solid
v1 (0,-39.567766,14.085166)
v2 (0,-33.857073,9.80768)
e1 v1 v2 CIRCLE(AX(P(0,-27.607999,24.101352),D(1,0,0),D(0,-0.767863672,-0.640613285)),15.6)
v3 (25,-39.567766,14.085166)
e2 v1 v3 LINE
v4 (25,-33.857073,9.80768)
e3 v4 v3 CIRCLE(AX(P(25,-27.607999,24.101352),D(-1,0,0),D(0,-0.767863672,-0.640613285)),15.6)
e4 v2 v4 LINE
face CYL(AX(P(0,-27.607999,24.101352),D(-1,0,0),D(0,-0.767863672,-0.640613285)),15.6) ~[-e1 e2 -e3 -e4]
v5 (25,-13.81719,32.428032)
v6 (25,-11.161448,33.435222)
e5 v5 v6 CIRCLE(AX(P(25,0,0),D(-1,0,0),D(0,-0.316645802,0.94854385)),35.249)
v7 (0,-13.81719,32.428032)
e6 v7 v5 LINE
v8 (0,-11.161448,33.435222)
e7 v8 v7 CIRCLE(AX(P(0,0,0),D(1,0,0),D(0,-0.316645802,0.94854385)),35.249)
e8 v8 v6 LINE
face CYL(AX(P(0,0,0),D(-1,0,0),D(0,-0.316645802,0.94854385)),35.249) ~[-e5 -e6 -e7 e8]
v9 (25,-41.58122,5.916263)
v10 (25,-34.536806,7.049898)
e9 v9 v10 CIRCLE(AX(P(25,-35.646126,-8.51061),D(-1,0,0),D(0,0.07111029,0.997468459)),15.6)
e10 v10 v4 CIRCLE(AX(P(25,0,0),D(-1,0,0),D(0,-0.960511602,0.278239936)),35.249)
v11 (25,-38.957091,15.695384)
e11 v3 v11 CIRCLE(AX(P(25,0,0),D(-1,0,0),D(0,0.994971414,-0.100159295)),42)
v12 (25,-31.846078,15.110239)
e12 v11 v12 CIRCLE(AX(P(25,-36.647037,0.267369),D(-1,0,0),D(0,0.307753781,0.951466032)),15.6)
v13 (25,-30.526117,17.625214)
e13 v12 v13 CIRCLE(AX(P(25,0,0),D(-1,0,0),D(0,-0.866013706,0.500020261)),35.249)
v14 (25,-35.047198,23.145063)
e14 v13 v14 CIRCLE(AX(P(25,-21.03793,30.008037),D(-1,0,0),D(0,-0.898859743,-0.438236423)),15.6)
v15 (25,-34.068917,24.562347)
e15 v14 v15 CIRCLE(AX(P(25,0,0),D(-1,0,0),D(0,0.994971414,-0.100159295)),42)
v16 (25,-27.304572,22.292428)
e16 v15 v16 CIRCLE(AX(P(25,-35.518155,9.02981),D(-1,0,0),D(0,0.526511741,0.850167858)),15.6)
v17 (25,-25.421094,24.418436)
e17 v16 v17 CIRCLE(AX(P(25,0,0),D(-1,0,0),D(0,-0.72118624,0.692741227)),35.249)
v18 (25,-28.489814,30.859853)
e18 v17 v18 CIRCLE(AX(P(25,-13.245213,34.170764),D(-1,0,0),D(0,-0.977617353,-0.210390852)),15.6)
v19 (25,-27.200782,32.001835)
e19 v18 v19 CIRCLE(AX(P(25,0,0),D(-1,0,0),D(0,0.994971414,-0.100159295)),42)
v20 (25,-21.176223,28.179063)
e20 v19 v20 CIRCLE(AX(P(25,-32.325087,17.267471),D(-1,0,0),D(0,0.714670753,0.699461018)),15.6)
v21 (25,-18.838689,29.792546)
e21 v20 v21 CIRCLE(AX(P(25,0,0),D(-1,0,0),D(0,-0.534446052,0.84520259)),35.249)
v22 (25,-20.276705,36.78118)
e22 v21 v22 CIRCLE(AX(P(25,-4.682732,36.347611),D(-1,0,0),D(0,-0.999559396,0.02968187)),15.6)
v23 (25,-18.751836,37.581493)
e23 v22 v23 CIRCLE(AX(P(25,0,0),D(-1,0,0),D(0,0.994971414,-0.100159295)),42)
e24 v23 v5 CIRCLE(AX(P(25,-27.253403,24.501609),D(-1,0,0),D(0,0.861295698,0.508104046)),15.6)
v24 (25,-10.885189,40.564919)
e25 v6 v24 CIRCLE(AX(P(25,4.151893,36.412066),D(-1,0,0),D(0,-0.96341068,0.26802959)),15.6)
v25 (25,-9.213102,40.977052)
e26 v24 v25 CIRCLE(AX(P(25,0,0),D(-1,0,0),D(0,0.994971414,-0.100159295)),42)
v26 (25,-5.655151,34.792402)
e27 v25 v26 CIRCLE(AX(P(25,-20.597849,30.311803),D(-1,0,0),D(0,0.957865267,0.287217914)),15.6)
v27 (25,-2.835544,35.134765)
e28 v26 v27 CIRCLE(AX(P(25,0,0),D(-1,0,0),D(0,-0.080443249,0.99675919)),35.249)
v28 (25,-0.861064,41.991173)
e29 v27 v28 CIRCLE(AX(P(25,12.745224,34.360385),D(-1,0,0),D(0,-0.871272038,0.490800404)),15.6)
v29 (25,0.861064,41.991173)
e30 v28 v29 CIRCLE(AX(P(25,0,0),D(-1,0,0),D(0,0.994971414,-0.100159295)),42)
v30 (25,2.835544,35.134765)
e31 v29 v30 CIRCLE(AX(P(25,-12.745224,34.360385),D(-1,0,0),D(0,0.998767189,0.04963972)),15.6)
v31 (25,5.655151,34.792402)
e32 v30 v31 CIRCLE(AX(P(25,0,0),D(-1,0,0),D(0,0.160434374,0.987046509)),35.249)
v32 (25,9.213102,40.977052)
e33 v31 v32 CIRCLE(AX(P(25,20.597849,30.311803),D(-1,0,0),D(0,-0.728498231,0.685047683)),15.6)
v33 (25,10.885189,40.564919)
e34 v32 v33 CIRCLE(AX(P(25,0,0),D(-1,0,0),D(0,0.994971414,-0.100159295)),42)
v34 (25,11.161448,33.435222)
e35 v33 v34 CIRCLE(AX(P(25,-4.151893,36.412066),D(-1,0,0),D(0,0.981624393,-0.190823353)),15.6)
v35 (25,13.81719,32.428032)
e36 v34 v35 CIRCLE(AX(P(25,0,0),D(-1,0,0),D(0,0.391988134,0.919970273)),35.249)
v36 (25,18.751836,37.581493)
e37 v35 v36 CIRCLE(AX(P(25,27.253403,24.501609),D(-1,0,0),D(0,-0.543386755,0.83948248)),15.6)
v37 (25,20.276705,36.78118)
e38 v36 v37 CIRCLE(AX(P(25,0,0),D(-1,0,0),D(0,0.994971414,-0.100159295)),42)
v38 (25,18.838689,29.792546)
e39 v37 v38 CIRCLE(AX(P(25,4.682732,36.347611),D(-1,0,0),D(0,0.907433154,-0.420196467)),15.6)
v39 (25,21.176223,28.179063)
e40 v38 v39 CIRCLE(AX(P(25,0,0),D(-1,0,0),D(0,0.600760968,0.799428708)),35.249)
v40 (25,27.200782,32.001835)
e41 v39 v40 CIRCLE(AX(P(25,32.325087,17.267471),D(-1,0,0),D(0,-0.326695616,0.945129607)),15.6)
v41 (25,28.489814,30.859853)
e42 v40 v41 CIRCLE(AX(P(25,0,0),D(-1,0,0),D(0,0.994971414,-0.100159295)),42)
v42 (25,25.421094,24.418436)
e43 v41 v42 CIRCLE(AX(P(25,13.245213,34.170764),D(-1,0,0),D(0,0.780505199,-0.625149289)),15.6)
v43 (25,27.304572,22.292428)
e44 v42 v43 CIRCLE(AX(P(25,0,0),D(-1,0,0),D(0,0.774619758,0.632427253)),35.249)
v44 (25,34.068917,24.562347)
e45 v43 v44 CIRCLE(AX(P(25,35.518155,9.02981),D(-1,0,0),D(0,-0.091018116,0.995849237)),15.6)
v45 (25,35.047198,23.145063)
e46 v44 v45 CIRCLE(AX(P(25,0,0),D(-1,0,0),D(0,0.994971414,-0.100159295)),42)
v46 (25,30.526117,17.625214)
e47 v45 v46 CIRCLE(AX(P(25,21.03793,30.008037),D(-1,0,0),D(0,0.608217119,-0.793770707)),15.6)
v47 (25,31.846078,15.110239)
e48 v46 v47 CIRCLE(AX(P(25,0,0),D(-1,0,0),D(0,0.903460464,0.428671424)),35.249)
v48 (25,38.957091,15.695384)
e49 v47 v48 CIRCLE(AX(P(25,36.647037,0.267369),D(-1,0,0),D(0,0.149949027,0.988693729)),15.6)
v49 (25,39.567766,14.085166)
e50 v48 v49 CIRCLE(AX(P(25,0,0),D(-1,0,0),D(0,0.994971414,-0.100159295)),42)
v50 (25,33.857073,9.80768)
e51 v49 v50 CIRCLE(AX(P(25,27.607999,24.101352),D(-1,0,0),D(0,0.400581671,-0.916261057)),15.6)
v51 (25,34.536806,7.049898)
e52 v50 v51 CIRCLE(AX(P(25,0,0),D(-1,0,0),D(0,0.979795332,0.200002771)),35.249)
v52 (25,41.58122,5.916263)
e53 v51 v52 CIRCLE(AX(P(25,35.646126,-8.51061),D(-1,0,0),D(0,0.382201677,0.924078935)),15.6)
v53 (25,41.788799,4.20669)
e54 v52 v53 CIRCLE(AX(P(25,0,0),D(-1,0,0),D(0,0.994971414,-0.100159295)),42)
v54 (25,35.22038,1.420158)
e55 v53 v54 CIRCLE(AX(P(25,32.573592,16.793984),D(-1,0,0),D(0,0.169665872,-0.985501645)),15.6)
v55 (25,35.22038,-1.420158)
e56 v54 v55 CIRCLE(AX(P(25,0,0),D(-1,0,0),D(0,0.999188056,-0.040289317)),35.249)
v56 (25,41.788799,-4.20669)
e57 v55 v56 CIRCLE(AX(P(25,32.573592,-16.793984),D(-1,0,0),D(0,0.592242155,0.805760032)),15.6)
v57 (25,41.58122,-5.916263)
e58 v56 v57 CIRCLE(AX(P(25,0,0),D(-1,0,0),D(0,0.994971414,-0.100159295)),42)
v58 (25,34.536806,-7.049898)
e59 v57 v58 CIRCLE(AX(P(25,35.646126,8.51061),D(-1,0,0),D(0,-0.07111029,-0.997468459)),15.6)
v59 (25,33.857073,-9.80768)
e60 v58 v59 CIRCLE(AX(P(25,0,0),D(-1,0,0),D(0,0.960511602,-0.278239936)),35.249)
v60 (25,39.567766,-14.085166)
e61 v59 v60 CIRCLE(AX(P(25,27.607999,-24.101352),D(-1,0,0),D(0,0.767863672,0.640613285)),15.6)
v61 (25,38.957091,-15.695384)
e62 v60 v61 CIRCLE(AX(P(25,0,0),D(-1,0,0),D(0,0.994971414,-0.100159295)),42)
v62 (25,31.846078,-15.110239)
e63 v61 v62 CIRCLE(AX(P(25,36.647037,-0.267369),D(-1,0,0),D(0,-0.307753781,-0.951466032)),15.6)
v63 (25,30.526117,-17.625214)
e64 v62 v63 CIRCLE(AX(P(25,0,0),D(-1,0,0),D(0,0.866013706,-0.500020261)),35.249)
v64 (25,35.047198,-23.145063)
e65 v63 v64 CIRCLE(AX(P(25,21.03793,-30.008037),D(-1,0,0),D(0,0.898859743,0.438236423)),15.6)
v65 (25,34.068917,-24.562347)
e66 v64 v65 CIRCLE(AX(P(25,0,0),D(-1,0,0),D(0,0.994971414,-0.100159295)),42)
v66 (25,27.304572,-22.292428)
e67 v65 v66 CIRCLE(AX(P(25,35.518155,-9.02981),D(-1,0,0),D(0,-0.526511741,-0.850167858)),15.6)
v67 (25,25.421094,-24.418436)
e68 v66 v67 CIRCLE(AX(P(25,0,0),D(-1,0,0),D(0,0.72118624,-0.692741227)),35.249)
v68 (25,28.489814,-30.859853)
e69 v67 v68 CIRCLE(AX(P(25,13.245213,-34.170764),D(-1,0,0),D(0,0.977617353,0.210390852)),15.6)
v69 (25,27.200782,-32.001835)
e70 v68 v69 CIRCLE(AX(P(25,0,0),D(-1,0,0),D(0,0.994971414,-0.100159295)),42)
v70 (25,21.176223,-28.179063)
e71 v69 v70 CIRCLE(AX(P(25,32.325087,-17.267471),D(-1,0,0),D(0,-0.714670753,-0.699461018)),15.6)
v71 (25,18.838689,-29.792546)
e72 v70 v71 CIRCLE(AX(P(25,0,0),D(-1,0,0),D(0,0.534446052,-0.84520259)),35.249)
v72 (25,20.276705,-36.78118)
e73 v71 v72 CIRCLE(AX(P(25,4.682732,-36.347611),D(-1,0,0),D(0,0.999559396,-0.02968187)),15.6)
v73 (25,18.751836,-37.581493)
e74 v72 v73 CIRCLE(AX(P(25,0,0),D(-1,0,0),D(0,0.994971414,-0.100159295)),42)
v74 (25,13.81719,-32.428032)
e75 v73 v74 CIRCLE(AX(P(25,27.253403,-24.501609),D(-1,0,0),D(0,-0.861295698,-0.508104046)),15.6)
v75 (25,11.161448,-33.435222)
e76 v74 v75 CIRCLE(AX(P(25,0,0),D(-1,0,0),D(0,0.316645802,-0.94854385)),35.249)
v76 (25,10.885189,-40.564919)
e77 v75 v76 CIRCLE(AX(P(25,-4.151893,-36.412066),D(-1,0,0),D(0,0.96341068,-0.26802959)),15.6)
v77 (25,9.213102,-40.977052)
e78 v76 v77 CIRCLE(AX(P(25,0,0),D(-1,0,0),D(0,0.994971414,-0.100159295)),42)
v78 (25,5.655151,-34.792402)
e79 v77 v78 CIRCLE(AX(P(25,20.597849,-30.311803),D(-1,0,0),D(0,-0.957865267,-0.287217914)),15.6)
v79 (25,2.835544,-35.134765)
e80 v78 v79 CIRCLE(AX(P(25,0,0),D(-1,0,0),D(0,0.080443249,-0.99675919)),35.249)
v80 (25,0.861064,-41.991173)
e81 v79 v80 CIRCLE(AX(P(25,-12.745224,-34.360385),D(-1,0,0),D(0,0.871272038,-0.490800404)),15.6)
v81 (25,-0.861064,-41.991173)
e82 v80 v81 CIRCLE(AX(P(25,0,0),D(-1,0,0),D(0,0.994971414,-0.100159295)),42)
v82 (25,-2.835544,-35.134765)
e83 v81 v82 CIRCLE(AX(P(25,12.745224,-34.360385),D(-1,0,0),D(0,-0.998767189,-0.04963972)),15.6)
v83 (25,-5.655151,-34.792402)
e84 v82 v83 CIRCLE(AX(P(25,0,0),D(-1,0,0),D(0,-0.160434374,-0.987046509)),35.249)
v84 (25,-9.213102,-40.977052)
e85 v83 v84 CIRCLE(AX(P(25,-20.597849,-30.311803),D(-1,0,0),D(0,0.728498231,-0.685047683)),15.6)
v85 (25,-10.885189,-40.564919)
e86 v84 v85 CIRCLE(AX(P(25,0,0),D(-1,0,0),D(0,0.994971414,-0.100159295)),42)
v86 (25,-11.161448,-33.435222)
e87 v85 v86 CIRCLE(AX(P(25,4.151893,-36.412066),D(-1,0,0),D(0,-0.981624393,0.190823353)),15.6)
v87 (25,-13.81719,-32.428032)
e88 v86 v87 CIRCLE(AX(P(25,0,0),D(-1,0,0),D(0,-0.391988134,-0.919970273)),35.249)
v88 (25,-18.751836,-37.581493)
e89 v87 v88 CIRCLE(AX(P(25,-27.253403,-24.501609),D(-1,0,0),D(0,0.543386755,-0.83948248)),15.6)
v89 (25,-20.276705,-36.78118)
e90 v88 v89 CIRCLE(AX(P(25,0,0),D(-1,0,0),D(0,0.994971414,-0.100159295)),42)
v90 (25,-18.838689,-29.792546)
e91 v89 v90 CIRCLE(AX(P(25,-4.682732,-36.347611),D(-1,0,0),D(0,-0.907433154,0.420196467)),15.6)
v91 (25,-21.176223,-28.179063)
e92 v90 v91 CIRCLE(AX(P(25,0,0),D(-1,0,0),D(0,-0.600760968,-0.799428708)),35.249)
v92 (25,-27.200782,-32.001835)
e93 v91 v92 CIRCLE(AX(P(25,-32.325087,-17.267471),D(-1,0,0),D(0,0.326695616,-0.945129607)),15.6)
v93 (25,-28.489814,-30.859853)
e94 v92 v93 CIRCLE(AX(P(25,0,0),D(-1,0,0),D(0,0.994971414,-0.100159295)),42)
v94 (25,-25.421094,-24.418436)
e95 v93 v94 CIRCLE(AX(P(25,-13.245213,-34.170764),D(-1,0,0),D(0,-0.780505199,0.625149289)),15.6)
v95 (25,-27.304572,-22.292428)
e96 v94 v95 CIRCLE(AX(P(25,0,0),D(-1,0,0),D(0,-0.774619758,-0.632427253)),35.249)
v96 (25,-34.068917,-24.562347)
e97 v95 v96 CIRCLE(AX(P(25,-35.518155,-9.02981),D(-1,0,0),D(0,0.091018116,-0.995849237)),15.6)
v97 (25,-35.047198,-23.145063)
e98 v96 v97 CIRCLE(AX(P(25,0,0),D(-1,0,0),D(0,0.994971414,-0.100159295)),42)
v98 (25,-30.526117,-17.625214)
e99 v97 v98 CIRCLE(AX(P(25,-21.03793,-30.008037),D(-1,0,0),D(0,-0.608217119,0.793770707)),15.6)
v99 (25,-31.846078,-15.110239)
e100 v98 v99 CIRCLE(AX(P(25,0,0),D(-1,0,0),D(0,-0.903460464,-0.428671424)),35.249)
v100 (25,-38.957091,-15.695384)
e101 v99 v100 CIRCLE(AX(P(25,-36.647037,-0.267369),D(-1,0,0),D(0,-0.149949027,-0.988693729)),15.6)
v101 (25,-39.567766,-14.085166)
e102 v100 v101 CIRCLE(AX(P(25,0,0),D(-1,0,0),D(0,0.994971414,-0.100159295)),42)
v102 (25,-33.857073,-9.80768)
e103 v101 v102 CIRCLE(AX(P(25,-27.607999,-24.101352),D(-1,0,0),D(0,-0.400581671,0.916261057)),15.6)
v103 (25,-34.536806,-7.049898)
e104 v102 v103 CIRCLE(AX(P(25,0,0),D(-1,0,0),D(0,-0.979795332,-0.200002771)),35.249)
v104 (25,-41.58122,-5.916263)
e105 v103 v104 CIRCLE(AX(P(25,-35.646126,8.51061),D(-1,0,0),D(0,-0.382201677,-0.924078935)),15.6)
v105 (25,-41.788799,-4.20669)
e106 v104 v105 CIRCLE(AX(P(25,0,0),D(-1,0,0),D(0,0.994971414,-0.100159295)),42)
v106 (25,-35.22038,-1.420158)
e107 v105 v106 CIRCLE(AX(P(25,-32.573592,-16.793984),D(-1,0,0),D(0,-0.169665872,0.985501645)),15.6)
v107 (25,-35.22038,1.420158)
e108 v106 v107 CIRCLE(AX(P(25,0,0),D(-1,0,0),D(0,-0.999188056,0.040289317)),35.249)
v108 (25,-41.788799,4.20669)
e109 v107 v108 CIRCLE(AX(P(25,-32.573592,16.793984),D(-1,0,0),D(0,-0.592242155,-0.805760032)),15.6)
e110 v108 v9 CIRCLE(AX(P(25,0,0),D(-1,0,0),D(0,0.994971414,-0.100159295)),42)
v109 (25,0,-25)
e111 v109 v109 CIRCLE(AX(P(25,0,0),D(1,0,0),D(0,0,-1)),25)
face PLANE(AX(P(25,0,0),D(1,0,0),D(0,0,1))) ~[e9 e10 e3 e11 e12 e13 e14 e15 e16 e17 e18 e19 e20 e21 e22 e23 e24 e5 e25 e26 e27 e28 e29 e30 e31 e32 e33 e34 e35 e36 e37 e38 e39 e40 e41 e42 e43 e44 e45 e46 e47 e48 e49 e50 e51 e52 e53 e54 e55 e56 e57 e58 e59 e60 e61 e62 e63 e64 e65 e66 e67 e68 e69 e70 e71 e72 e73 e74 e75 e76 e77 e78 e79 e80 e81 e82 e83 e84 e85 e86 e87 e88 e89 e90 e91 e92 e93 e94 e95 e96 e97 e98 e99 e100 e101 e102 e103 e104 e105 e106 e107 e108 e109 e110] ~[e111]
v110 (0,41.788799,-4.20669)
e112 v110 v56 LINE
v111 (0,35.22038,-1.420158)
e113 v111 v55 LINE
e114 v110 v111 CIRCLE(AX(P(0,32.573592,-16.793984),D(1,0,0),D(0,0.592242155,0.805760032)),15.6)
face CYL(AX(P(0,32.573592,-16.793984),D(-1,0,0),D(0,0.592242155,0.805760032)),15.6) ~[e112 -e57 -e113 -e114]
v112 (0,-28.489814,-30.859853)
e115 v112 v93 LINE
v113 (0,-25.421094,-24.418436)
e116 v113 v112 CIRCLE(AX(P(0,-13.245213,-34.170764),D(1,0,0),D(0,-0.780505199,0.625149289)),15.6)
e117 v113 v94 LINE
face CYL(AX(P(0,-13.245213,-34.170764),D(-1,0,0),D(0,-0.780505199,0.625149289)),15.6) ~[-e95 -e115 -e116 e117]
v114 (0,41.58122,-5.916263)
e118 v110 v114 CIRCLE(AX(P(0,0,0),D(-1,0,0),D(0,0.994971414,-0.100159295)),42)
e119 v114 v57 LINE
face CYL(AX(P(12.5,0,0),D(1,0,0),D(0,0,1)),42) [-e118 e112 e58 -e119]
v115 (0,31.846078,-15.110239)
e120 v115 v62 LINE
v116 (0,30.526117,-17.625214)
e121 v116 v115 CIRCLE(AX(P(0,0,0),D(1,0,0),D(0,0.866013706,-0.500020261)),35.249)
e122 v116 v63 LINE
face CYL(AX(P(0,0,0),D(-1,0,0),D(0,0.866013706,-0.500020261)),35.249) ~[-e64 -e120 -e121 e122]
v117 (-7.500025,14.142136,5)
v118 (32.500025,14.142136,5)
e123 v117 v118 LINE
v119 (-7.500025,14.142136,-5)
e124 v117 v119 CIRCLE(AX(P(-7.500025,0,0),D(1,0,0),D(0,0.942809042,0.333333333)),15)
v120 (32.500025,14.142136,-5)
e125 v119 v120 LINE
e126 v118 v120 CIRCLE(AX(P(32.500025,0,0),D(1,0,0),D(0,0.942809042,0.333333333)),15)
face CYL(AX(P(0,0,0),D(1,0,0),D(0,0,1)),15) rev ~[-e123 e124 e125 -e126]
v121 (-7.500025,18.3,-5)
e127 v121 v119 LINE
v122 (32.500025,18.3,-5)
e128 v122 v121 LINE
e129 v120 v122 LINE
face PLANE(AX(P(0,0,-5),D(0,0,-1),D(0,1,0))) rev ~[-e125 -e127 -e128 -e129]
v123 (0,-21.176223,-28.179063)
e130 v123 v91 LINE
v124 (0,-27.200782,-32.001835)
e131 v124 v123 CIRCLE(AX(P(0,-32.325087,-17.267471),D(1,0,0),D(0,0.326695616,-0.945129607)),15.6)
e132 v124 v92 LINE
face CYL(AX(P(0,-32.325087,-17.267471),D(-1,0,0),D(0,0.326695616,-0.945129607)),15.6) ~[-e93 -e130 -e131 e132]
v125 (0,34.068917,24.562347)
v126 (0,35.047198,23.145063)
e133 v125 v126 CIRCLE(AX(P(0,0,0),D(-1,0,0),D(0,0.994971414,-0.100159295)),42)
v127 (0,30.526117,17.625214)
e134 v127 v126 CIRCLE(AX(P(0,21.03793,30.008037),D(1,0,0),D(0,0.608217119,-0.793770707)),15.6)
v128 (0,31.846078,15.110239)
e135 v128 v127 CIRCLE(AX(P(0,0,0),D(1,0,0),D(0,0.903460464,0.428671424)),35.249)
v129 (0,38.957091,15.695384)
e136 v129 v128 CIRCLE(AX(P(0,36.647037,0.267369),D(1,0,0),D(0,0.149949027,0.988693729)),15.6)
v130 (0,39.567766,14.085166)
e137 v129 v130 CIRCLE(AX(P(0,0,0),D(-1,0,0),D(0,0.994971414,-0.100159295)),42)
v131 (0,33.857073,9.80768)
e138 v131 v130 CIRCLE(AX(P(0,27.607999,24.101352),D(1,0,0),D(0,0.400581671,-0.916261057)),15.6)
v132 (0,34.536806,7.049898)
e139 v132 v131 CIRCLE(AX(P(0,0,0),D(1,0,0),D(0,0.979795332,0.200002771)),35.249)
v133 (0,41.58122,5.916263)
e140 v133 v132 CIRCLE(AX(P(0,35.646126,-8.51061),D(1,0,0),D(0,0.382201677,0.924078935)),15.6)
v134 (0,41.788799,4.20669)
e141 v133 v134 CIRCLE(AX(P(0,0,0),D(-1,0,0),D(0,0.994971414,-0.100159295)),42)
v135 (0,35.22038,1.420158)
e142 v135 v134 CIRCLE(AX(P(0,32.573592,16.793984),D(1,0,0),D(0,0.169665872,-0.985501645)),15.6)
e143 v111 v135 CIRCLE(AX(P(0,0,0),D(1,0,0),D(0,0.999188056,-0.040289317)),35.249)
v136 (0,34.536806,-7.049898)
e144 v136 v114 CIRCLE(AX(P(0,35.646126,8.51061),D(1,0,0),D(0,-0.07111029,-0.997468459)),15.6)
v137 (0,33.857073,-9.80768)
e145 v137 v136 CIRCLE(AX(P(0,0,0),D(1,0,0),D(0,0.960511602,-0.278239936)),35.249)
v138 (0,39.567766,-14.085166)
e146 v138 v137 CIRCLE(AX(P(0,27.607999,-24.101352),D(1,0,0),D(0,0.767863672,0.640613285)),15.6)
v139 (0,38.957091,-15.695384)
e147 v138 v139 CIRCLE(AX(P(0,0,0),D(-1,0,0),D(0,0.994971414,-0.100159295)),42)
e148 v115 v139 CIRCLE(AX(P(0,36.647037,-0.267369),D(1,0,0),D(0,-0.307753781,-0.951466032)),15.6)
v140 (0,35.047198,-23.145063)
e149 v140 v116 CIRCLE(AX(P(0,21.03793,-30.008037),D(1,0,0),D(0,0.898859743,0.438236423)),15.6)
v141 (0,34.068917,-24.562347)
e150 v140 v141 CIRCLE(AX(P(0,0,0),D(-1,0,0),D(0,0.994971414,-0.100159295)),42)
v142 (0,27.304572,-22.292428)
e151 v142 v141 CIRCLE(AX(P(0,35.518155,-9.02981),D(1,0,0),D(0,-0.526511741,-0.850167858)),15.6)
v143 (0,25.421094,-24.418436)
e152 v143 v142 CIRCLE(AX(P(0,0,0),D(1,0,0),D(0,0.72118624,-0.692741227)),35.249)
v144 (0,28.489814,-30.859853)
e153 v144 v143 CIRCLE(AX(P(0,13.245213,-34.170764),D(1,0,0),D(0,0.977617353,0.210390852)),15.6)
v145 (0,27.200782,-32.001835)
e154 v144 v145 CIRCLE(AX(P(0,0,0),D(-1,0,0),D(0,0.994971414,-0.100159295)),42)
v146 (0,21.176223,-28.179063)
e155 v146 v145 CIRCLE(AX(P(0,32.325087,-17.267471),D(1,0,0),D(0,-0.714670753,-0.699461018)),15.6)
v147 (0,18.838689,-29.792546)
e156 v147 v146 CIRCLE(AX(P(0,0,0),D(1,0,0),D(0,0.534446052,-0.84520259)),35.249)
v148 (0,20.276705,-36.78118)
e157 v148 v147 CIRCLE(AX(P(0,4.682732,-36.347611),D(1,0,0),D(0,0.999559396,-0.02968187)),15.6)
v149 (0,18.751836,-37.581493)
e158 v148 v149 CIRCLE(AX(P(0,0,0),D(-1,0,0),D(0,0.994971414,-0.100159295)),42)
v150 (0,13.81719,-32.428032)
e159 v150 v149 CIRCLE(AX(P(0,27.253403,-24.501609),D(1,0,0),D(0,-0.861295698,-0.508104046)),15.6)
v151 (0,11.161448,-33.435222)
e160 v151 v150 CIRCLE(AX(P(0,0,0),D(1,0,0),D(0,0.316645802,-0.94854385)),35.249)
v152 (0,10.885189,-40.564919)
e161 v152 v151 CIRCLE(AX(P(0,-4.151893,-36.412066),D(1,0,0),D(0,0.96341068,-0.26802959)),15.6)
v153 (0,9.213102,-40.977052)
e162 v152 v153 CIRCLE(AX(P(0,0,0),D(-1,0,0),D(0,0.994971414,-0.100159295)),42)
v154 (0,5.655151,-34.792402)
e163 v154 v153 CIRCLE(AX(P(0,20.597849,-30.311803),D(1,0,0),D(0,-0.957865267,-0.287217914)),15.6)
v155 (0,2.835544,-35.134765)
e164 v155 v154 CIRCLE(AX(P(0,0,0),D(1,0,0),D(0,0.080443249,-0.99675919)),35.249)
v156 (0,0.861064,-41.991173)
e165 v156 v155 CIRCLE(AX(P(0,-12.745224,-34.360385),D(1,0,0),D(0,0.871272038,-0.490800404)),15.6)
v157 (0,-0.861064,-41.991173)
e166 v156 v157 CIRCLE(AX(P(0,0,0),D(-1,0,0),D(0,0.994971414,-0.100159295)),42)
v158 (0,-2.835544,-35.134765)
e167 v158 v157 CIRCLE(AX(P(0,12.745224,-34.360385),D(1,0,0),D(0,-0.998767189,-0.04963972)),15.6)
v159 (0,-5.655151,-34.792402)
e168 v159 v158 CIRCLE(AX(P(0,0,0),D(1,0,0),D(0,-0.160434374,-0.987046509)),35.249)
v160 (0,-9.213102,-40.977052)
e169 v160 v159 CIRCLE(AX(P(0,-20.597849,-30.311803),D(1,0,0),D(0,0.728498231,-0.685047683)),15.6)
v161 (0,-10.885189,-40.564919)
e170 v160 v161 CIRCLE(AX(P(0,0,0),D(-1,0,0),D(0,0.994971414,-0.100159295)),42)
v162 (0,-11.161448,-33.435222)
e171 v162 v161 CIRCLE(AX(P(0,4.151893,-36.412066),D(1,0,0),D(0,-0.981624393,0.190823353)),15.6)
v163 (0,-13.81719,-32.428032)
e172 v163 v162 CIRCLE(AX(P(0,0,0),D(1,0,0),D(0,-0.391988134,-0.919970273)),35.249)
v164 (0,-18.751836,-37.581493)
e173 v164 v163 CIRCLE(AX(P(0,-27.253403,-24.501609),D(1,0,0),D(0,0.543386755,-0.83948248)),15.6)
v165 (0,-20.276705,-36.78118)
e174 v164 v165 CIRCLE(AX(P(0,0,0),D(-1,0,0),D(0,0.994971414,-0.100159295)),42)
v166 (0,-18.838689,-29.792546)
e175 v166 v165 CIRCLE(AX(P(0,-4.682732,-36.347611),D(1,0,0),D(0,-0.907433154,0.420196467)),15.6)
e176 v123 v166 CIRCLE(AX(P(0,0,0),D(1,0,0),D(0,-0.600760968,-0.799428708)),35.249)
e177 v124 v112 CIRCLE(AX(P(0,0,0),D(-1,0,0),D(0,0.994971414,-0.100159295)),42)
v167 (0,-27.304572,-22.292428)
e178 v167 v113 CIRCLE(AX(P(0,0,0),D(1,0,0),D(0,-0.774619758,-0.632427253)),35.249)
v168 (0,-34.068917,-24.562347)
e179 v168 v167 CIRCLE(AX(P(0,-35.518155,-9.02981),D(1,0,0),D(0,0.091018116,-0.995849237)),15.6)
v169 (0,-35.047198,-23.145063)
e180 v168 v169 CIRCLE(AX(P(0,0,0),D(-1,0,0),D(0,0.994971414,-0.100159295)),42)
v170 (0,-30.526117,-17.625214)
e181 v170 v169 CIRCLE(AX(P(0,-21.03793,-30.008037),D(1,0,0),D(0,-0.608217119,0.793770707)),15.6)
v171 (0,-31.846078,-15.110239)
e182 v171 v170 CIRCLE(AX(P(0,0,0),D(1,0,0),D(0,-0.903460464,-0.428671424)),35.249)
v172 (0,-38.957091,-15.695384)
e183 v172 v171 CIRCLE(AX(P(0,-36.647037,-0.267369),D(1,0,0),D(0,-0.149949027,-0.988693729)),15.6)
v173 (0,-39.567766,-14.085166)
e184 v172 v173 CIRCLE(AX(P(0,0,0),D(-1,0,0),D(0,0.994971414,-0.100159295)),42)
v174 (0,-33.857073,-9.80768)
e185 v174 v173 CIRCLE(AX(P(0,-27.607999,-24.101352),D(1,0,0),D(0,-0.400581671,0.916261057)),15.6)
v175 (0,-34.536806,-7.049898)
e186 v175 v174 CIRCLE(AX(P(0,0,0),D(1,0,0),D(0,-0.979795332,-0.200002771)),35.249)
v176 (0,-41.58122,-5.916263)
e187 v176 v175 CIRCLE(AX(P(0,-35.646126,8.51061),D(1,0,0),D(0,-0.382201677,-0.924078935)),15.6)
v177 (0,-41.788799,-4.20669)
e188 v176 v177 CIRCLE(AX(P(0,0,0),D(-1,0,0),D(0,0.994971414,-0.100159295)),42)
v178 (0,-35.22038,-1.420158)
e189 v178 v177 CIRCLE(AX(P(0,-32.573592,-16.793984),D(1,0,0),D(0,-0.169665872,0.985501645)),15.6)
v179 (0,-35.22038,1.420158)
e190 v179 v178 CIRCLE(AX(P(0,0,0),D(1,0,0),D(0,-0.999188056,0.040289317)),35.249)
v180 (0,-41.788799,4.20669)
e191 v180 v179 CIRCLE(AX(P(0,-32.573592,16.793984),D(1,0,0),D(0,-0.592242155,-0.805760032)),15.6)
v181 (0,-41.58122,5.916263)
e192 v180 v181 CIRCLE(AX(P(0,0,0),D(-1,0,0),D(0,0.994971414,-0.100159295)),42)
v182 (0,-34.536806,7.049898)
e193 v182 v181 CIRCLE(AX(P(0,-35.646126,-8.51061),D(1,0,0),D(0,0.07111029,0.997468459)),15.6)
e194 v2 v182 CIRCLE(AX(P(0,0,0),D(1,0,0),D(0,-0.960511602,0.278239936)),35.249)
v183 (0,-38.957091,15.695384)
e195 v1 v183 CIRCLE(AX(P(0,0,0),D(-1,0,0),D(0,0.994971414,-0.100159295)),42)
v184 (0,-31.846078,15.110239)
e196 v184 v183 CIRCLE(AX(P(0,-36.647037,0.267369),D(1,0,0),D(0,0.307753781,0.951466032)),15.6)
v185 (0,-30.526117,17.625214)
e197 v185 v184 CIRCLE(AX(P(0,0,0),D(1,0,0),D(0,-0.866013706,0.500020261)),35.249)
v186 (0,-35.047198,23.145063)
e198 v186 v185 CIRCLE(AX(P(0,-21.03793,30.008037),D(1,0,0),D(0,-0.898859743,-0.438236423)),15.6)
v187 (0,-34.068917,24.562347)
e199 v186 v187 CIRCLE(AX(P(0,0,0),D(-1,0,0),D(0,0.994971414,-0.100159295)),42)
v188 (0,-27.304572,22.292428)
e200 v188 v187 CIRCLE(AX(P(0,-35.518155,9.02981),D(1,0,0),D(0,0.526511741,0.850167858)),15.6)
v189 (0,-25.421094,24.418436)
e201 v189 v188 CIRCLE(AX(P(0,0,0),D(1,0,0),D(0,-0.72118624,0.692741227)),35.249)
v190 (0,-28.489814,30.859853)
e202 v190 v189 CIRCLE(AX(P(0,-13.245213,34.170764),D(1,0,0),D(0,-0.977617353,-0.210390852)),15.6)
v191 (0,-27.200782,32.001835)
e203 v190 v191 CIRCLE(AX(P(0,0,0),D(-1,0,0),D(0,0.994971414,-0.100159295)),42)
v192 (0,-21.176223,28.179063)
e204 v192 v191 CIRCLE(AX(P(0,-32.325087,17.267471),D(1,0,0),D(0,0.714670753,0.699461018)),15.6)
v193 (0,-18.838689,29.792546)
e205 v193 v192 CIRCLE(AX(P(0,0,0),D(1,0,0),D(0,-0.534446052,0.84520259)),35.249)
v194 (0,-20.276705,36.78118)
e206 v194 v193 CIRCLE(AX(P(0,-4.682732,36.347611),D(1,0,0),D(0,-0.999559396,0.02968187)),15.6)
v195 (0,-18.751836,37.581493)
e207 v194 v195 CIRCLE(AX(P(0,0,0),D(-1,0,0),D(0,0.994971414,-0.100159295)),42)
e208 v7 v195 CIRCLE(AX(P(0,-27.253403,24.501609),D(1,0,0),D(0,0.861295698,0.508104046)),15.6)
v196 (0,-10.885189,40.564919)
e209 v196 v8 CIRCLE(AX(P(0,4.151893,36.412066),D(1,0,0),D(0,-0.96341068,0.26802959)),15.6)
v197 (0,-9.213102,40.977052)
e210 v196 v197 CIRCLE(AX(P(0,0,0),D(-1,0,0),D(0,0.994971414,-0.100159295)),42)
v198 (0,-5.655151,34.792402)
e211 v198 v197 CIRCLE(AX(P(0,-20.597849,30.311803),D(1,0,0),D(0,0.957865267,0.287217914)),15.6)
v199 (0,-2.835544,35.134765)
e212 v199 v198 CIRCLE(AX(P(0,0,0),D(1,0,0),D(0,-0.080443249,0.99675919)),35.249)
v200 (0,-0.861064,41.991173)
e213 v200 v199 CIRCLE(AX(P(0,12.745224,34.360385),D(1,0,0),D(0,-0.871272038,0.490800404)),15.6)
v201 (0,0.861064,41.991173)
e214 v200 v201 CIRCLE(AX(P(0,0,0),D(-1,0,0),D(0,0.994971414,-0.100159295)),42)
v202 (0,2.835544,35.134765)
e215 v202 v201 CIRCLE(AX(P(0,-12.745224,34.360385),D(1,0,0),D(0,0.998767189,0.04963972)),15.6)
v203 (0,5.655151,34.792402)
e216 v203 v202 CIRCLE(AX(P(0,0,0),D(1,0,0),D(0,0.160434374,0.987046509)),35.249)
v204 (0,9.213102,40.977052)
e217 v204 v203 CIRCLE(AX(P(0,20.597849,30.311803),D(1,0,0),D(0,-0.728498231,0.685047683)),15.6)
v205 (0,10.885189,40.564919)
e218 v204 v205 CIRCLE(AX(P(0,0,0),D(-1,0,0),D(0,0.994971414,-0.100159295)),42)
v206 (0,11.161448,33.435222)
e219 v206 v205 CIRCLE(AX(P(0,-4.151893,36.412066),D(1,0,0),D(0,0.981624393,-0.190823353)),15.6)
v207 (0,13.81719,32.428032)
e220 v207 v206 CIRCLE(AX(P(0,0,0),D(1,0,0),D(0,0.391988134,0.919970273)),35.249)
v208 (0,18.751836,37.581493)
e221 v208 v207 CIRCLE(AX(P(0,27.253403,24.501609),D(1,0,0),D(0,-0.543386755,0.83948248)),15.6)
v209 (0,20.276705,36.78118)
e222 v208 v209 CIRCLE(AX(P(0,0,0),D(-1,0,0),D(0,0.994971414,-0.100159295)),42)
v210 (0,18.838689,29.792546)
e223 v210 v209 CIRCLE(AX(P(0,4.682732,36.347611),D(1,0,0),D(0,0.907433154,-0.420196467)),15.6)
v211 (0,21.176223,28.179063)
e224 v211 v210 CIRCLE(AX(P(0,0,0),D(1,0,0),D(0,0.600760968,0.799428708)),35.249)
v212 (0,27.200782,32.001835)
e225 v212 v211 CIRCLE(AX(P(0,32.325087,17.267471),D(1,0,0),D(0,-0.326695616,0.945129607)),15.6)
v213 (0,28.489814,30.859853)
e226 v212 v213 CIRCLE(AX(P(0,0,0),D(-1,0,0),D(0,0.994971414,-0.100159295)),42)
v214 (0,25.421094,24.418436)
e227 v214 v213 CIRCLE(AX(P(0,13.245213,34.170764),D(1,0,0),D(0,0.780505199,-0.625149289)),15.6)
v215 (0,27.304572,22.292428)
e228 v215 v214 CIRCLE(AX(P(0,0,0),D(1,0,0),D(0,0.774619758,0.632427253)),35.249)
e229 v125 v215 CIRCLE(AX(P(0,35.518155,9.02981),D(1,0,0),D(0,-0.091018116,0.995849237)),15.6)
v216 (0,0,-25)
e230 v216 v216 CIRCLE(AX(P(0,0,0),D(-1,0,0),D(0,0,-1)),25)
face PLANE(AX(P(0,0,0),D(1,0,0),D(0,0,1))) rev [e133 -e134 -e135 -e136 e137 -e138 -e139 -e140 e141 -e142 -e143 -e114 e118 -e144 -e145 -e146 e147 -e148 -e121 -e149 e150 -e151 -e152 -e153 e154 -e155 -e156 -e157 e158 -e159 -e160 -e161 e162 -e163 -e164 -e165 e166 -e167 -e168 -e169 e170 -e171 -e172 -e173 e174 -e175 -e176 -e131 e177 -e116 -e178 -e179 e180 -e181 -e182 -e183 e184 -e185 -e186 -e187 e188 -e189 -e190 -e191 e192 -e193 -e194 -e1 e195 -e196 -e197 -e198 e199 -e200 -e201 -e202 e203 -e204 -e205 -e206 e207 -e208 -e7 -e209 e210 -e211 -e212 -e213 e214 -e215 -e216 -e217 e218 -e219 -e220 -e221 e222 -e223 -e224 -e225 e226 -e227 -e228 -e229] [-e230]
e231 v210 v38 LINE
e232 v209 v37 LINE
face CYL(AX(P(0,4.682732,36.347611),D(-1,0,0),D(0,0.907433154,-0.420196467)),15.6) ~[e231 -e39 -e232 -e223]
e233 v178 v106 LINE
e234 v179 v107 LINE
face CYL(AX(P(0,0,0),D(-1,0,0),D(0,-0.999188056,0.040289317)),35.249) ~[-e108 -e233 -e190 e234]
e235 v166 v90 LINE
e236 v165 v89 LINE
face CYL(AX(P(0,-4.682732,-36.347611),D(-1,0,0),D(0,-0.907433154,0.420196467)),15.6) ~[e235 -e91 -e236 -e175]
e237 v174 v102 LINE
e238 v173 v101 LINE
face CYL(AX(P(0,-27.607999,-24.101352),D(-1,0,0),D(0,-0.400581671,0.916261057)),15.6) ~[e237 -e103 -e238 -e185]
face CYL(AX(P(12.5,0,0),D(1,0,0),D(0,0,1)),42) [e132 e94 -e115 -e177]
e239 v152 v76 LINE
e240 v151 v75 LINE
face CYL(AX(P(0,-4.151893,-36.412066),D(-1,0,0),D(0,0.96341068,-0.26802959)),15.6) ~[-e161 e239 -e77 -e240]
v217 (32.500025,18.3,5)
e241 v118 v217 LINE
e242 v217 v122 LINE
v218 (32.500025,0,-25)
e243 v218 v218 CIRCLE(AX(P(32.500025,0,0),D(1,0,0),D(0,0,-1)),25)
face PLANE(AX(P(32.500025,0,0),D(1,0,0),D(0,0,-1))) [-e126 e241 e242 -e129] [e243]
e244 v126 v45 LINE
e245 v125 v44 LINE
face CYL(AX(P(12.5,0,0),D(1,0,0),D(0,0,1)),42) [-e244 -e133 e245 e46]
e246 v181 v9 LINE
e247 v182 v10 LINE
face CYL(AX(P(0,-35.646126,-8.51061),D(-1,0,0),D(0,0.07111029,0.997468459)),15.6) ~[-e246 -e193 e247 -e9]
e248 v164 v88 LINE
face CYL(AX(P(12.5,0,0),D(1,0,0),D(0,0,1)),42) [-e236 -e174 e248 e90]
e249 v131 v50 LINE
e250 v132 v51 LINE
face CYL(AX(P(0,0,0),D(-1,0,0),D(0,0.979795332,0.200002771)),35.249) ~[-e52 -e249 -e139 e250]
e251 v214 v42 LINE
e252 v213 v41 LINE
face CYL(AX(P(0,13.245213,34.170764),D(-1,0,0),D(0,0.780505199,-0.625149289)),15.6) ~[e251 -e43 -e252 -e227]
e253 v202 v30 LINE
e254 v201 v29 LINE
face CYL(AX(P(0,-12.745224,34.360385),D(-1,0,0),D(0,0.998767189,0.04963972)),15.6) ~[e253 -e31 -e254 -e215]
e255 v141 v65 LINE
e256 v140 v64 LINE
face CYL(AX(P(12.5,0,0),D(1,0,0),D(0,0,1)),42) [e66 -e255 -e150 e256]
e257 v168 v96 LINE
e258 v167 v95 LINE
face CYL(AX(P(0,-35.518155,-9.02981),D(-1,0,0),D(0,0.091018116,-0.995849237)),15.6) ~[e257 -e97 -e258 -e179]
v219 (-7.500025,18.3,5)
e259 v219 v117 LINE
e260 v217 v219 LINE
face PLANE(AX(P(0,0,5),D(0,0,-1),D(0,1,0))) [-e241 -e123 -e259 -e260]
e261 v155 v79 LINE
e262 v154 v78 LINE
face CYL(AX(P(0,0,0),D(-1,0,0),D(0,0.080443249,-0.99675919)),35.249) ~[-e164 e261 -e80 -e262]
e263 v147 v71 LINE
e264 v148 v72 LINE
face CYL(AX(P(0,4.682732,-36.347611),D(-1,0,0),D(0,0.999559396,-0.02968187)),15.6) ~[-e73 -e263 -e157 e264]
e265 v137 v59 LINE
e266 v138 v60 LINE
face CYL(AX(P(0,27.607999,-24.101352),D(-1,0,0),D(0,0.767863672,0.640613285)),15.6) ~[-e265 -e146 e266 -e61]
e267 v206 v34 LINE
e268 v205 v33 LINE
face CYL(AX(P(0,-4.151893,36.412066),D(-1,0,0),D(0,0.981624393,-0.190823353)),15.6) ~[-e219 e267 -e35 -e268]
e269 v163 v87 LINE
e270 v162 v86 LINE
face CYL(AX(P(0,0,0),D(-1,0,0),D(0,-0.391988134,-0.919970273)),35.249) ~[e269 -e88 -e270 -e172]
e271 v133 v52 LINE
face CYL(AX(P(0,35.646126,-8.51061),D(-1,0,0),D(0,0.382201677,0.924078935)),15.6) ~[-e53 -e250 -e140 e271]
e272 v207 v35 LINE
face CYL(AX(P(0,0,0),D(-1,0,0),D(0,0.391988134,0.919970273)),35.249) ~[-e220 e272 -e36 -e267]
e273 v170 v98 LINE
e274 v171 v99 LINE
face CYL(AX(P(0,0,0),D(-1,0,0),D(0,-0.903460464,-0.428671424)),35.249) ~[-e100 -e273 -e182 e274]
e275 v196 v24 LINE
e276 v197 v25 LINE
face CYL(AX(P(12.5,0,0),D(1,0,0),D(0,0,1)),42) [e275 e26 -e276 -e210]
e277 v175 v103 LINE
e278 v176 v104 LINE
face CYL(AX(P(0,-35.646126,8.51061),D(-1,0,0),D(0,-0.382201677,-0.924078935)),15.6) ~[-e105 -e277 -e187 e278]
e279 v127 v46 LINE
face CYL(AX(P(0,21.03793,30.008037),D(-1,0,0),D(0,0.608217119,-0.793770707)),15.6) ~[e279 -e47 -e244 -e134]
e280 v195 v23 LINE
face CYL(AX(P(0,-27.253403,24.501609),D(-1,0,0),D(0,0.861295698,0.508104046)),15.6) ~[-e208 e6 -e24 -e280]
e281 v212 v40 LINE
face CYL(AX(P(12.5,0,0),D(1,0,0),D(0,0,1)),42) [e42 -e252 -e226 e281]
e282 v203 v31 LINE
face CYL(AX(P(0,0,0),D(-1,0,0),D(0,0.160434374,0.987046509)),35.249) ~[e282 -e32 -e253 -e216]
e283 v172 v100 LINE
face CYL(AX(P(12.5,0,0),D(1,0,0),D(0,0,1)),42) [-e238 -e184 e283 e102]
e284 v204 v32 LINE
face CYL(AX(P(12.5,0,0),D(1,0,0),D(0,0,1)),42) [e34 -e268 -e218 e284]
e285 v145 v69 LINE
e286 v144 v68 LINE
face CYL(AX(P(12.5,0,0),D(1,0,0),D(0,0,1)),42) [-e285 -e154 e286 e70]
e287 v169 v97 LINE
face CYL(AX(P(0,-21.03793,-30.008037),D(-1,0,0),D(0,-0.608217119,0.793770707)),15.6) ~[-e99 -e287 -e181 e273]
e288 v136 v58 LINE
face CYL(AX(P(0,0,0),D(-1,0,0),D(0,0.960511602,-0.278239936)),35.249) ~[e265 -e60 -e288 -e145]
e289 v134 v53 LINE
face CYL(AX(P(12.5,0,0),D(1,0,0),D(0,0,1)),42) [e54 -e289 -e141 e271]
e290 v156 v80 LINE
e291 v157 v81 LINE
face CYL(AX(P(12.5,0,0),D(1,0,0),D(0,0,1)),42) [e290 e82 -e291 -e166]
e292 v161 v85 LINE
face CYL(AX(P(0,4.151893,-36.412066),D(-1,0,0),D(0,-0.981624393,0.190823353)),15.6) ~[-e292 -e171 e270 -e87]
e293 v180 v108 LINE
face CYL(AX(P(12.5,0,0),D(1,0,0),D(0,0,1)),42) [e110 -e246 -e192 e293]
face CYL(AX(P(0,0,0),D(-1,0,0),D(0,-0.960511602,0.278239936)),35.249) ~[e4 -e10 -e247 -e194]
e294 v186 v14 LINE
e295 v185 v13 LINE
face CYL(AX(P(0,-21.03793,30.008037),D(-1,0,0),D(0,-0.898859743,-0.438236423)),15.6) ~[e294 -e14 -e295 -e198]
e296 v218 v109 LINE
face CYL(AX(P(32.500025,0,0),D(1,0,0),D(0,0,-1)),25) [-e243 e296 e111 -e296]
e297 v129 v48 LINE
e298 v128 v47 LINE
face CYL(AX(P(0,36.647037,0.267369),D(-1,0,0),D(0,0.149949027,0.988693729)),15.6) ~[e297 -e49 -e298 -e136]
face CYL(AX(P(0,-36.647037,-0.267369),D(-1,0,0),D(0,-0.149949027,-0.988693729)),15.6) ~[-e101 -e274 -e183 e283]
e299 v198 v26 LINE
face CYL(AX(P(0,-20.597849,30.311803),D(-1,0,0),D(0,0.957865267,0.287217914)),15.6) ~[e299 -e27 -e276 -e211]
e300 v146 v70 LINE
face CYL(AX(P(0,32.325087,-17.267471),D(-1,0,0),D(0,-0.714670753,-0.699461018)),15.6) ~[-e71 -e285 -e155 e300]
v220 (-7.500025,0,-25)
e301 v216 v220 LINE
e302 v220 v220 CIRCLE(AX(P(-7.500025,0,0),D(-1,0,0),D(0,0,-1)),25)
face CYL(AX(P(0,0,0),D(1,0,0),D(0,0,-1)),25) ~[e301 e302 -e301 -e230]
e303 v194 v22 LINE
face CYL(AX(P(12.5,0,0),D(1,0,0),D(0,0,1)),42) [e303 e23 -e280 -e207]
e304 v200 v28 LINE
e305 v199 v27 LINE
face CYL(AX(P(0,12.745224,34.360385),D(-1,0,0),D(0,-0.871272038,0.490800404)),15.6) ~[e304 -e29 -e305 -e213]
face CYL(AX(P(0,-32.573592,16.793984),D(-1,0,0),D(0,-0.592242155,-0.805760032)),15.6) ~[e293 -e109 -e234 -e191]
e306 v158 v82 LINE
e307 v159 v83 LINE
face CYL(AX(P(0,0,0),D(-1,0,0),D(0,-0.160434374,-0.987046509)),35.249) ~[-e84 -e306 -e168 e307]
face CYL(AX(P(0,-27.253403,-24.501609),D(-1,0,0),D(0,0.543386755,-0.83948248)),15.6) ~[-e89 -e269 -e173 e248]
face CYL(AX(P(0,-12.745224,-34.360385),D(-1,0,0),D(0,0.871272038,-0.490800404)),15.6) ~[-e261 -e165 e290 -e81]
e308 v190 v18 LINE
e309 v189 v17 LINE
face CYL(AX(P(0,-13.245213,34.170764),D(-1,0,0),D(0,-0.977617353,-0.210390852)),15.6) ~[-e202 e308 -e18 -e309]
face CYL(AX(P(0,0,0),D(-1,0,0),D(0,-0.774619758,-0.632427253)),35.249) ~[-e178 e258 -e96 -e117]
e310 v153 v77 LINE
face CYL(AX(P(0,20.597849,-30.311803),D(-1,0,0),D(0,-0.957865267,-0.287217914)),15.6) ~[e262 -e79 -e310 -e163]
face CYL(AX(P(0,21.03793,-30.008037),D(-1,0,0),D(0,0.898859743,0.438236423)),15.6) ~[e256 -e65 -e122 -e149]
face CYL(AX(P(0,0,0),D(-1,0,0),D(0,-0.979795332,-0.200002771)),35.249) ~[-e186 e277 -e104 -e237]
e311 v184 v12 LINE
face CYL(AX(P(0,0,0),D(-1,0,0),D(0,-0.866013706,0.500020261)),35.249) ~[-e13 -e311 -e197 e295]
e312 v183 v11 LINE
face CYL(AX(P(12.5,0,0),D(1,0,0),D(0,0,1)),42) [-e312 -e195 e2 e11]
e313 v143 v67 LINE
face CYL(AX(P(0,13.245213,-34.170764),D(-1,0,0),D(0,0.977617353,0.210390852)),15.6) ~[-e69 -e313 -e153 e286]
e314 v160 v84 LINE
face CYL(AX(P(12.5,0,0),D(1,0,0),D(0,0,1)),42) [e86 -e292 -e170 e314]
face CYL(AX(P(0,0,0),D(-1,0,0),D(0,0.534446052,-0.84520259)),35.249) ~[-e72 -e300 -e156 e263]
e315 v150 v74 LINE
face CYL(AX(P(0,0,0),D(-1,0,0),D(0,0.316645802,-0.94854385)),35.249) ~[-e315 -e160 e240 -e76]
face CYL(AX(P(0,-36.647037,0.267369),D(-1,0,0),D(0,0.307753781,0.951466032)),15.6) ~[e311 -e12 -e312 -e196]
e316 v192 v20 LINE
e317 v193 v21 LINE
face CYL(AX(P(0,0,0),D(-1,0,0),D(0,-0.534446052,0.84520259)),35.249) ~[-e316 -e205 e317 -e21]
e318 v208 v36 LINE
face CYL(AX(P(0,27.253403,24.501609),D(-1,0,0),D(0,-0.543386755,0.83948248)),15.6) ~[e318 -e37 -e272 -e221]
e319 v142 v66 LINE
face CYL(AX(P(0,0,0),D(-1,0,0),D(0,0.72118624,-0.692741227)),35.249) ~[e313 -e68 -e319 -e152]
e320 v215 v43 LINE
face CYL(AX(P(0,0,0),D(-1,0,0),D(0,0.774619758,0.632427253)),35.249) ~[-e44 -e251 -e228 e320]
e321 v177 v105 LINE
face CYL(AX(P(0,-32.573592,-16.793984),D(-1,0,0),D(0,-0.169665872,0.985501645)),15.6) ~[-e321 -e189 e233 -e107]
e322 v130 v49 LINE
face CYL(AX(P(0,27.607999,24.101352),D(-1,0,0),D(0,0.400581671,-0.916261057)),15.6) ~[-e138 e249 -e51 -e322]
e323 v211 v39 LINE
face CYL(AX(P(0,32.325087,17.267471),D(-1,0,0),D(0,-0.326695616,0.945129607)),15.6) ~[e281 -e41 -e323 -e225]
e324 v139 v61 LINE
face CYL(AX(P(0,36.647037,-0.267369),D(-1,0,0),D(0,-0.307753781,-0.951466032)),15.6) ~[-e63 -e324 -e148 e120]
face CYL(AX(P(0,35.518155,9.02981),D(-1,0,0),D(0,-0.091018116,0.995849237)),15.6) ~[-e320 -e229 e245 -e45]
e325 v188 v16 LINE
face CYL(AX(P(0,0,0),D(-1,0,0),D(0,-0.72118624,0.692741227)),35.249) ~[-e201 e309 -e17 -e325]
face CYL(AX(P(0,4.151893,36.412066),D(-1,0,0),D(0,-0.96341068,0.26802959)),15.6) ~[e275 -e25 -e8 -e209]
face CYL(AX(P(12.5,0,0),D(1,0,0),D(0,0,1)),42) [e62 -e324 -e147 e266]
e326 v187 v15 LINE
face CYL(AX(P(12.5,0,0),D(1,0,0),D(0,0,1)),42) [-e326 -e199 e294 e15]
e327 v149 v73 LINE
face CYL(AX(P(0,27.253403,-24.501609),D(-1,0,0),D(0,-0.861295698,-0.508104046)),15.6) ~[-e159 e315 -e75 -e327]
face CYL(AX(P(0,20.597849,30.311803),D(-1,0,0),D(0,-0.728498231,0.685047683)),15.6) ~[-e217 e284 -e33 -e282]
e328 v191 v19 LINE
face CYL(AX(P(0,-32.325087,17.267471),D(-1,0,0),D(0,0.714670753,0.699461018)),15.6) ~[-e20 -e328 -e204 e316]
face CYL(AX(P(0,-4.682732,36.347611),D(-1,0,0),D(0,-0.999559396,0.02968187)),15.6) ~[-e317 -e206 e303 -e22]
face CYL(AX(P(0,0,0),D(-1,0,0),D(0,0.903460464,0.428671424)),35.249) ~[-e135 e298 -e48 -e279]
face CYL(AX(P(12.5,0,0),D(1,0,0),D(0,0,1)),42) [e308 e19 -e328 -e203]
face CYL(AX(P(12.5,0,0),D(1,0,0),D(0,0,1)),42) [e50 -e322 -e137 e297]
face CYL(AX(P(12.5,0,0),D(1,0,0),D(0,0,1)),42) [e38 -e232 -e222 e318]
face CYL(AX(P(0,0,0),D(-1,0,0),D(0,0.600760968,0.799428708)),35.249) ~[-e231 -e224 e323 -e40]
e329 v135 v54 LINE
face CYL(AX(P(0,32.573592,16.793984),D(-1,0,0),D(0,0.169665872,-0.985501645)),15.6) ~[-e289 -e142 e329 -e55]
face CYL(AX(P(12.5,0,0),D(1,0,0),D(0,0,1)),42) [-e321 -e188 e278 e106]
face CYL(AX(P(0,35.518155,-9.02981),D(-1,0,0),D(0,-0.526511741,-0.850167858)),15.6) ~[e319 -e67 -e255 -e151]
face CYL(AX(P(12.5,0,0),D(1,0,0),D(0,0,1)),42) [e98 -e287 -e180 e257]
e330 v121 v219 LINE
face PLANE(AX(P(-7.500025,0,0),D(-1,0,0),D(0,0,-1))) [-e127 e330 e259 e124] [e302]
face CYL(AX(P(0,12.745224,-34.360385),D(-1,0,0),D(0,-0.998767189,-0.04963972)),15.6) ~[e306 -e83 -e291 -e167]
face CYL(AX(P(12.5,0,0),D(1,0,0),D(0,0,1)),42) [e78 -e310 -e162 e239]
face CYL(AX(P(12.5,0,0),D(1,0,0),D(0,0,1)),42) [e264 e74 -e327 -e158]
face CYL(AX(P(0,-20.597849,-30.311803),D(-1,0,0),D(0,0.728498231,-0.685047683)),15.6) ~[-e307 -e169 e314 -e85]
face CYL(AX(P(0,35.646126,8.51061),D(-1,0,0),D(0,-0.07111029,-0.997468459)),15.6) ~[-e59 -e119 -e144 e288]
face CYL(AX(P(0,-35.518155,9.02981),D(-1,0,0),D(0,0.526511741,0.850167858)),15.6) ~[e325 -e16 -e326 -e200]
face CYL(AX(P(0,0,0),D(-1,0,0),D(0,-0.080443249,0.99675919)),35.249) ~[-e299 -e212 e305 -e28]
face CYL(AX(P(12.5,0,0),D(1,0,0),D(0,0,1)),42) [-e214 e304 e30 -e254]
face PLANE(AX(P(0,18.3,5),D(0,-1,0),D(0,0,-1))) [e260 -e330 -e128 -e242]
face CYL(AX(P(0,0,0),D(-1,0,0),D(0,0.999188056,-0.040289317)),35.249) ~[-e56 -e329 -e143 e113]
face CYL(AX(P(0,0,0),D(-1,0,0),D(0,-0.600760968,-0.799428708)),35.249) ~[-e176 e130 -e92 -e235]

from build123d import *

# Parameters (mm, degrees)
BASPROSKE_W       = 25
BASPROSKE_H       = 42
TOOTHCUT_DEPTH    = 65.443773943
TEETHCUTS_COUNT   = 26
TEETHCUTS_ANGLE   = 346.153846154
HUBNEABOTSKE_R    = 25
HUBNEARBOTH_DEPTH = 7.5000254
HUBFAR_START      = 7.5000254
HUBFARSKE_R       = 25
HUBFAR_DEPTH      = 7.5000254
BORSKE_R          = 15
BORE_DEPTH        = 40.0000508
KEYSKE_W          = 10
KEYSKE_H          = 18.3
KEYWAY_DEPTH      = 40.0000508


with BuildPart() as part:
    # BasProSke → Base-Revolve (revolve)
    with BuildSketch(Plane(origin=(0, 0, 0), x_dir=(1, 0, 0), z_dir=(0, 1, 0)), mode=Mode.PRIVATE) as base_revolve_sk:
        with Locations((12.5, 21)):
            Rectangle(BASPROSKE_W, BASPROSKE_H)
    revolve(base_revolve_sk.sketch.rotate(Axis((-10, 0, 0), (1, 0, 0)), 180), axis=Axis((-10, 0, 0), (1, 0, 0)))

    # TooCutSke → ToothCut (cut, through all)
    with BuildSketch(Plane(origin=(0, 0, 0), x_dir=(0, 0, -1), z_dir=(1, 0, 0))):
        with BuildLine():
            ThreePointArc((1.420158149, 35.22037978), (0, 35.249), (-1.420158149, 35.22037978))
            ThreePointArc((-1.420158149, 35.22037978), (-2.438615981, 38.679606797), (-4.224127309, 41.812569804))
            ThreePointArc((-4.224127309, 41.812569804), (0, 42.0254), (4.224127309, 41.812569804))
            ThreePointArc((4.224127309, 41.812569804), (2.438615981, 38.679606797), (1.420158149, 35.22037978))
        make_face()
    toothcut = extrude(amount=TOOTHCUT_DEPTH, mode=Mode.SUBTRACT)

    # TeethCuts: ToothCut ×26 about axis
    teethcuts_axis = Axis((-10, 0, 0), (1, 0, 0))
    for i in range(1, TEETHCUTS_COUNT):
        add(toothcut.rotate(teethcuts_axis, i * TEETHCUTS_ANGLE / (TEETHCUTS_COUNT - 1)), mode=Mode.SUBTRACT)

    # HubNeaBotSke → HubNearBoth (add)
    with BuildSketch(Plane.ZY):
        with Locations(Location((0, 0, 0), (0, 0, 180))):
            Circle(HUBNEABOTSKE_R)
    extrude(amount=HUBNEARBOTH_DEPTH)

    # HubFarSke → HubFar (add)
    with BuildSketch(Plane(origin=(25, 0, 0), x_dir=(0, 0, -1), z_dir=(1, 0, 0)).offset(HUBFAR_START)):
        Circle(HUBFARSKE_R)
    extrude(amount=-HUBFAR_DEPTH)

    # BorSke → Bore (cut, symmetric)
    with BuildSketch(Plane(origin=(0, 0, 0), x_dir=(0, 0, -1), z_dir=(1, 0, 0))):
        with Locations(Location((0, 0, 0), (0, 0, 180))):
            Circle(BORSKE_R)
    extrude(amount=BORE_DEPTH, both=True, mode=Mode.SUBTRACT)

    # KeySke → Keyway (cut, symmetric)
    with BuildSketch(Plane(origin=(0, 0, 0), x_dir=(0, 0, -1), z_dir=(1, 0, 0))):
        with Locations((0, 9.15)):
            Rectangle(KEYSKE_W, KEYSKE_H)
    extrude(amount=KEYWAY_DEPTH, both=True, mode=Mode.SUBTRACT)


solid = part.part
